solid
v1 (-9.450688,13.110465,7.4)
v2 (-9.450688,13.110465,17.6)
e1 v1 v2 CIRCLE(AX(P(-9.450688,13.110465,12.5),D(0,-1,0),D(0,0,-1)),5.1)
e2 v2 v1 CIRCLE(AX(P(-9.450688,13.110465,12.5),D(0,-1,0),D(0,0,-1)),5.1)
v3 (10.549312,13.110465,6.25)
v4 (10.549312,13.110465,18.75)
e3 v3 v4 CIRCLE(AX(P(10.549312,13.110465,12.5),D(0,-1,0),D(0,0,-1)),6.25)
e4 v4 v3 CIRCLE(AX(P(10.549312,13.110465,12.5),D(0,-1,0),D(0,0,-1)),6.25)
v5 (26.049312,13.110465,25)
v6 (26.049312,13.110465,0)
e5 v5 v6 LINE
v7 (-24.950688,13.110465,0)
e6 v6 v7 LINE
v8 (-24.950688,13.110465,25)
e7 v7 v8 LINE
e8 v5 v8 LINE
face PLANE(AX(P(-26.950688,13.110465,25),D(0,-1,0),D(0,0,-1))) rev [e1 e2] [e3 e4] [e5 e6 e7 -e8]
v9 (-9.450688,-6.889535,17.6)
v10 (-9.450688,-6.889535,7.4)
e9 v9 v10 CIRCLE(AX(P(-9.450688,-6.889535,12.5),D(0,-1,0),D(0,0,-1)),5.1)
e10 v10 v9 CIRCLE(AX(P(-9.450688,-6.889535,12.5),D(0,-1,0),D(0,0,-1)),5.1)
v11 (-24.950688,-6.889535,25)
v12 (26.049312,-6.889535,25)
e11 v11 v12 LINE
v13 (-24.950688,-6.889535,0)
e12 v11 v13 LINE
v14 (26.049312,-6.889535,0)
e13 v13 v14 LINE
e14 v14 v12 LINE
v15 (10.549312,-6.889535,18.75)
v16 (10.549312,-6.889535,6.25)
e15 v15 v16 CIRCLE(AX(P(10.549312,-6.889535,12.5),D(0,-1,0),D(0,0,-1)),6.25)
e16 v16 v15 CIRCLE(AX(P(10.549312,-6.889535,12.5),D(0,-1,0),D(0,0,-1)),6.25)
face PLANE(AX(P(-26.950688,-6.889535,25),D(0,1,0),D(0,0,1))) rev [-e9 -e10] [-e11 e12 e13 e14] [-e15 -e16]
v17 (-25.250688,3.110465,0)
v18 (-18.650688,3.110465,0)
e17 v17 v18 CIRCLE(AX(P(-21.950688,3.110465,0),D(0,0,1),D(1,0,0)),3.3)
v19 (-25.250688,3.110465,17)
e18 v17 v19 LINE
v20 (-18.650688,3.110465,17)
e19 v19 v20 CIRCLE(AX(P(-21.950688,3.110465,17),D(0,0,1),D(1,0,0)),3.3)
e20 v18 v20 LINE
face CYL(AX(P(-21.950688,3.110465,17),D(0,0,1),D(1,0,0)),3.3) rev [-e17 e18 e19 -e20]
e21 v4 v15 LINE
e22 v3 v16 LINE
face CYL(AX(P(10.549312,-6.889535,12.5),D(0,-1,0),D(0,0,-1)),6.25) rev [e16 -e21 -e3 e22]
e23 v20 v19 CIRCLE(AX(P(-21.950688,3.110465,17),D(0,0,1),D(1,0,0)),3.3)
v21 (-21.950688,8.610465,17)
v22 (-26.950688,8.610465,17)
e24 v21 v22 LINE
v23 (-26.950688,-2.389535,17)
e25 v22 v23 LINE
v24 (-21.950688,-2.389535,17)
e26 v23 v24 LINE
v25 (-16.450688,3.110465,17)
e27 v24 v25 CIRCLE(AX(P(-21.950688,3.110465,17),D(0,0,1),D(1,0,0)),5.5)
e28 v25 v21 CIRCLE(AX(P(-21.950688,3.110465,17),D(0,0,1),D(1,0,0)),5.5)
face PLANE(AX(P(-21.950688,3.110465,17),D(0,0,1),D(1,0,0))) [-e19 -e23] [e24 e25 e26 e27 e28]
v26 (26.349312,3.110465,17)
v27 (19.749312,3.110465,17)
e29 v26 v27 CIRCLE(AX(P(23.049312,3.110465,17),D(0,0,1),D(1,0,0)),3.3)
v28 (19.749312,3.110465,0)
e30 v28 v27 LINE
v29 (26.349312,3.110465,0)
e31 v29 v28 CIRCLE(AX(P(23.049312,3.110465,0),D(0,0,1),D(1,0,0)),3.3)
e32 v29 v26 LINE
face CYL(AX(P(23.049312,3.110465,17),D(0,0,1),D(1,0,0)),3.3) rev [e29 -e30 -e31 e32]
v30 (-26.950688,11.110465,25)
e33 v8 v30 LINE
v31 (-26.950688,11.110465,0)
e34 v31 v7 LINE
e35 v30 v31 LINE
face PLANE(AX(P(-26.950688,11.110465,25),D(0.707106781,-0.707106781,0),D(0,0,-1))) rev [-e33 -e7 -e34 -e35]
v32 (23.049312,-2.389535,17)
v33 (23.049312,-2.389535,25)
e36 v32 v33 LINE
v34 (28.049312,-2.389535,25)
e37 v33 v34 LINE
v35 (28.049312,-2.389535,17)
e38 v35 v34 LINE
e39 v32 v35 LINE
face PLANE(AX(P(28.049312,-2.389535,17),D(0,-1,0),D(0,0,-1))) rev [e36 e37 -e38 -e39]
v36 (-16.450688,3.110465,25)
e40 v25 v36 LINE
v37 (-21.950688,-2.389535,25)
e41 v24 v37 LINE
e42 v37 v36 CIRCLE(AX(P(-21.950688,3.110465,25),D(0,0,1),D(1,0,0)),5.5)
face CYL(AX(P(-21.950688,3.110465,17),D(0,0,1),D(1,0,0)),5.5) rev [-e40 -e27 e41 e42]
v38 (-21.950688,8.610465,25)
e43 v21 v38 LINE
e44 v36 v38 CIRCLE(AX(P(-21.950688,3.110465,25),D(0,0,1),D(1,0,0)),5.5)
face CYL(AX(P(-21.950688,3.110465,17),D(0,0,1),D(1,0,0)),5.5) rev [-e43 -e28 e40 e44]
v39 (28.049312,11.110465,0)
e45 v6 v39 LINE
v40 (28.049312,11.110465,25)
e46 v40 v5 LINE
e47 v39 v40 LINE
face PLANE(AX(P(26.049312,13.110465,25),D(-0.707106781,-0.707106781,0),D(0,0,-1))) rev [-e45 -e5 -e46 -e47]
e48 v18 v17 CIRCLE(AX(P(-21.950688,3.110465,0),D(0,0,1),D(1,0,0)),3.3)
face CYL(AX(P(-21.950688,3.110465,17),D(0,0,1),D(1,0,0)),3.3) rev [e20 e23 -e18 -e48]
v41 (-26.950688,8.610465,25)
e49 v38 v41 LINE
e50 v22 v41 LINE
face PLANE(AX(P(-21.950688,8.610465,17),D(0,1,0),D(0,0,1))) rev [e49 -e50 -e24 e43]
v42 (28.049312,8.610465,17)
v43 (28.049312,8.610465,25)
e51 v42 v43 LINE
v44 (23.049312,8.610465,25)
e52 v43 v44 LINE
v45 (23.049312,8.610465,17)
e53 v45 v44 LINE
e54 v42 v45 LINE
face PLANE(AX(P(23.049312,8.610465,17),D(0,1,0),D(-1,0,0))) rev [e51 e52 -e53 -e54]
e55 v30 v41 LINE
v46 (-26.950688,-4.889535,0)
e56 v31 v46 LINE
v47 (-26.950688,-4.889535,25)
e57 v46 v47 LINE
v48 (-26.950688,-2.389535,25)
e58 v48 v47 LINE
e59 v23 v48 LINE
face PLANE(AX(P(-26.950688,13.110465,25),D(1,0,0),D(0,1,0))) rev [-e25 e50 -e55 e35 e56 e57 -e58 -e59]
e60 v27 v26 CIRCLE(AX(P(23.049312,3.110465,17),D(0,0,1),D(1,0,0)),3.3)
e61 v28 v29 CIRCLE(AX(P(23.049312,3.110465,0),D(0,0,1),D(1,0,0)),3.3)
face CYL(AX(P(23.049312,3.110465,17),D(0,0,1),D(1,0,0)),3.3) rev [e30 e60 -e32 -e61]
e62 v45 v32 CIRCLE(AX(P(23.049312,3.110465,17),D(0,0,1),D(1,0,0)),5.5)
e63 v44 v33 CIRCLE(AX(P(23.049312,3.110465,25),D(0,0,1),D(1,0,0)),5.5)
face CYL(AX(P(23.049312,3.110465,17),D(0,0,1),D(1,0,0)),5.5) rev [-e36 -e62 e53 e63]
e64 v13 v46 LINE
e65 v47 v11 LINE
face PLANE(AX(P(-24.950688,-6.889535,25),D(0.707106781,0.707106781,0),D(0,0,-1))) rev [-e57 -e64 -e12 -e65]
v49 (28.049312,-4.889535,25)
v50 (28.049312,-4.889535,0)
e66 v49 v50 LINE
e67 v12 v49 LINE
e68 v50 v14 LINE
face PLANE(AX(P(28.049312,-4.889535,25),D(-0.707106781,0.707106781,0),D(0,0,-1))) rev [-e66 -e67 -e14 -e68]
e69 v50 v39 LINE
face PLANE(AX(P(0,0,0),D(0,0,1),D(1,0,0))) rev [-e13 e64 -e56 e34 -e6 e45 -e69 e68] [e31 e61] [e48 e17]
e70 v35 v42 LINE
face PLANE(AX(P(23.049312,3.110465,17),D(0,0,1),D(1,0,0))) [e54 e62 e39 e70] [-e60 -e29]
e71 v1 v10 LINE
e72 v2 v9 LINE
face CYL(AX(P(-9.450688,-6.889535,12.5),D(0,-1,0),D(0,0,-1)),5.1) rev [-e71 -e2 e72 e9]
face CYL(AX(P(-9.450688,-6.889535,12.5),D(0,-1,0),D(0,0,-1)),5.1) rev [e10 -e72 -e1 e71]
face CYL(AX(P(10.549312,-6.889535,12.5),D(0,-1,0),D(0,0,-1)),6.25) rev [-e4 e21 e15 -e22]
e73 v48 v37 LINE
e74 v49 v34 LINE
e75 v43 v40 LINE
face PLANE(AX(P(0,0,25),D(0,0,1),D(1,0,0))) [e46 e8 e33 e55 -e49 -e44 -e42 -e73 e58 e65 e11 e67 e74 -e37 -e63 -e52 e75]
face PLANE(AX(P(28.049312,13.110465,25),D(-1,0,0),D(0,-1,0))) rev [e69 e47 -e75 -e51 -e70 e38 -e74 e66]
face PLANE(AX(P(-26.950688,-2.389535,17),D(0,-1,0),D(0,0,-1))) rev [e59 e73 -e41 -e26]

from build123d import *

# Parameters (mm, degrees)
SKETCH1_W              = 55
SKETCH1_H              = 20
BOSS_EXTRUDE1_DEPTH    = 25
CHAMFER1_SIZE          = 2
CUT_EXTRUDE1_DEPTH     = 8
HOLE1_D                = 6.6
M12_TAPPED_HOLE1_D     = 10.2
M14X1_5_TAPPED_HOLE1_D = 12.5


with BuildPart() as part:
    # Sketch1 → Boss-Extrude1 (new body)
    with BuildSketch(Plane.XY):
        with Locations((0.549312304, 3.110465116)):
            Rectangle(SKETCH1_W, SKETCH1_H)
    extrude(amount=BOSS_EXTRUDE1_DEPTH)

    # Chamfer1
    chamfer1_edges = [part.edges().sort_by_distance(p)[0] for p in [
        (-26.950687696, 13.110465116, 12.5),
        (28.049312304, 13.110465116, 12.5),
        (28.049312304, -6.889534884, 12.5),
        (-26.950687696, -6.889534884, 12.5),
    ]]
    chamfer(chamfer1_edges, length=CHAMFER1_SIZE)

    # Sketch2 → Cut-Extrude1 (cut)
    with BuildSketch(Plane.XY.offset(25)):
        with BuildLine():
            Line((-21.950687696, 8.610465116), (-26.950687696, 8.610465116))
            Line((-26.950687696, 8.610465116), (-26.950687696, -2.389534884))
            Line((-26.950687696, -2.389534884), (-21.950687696, -2.389534884))
            ThreePointArc((-21.950687696, -2.389534884), (-16.450687696, 3.110465116), (-21.950687696, 8.610465116))
        make_face()
        with BuildLine():
            Line((23.049312304, 8.610465116), (28.049312304, 8.610465116))
            Line((28.049312304, 8.610465116), (28.049312304, -2.389534884))
            Line((28.049312304, -2.389534884), (23.049312304, -2.389534884))
            ThreePointArc((23.049312304, -2.389534884), (17.549312304, 3.110465116), (23.049312304, 8.610465116))
        make_face()
    extrude(amount=-CUT_EXTRUDE1_DEPTH, mode=Mode.SUBTRACT)

    # Hole1 (through all)
    with Locations(Plane.XY.offset(17)):
        with Locations((-21.950687696, 3.110465116), (23.049312304, 3.110465116)):
            Hole(HOLE1_D / 2)

    # M12 Tapped Hole1 (through all)
    with Locations(Plane(origin=(0, -6.889534884, 0), x_dir=(-1, 0, 0), z_dir=(0, -1, 0))):
        with Locations((9.450687696, -12.5)):
            Hole(M12_TAPPED_HOLE1_D / 2)

    # M14x1.5 Tapped Hole1 (through all)
    with Locations(Plane(origin=(0, -6.889534884, 0), x_dir=(-1, 0, 0), z_dir=(0, -1, 0))):
        with Locations((-10.549312304, -12.5)):
            Hole(M14X1_5_TAPPED_HOLE1_D / 2)


solid = part.part
